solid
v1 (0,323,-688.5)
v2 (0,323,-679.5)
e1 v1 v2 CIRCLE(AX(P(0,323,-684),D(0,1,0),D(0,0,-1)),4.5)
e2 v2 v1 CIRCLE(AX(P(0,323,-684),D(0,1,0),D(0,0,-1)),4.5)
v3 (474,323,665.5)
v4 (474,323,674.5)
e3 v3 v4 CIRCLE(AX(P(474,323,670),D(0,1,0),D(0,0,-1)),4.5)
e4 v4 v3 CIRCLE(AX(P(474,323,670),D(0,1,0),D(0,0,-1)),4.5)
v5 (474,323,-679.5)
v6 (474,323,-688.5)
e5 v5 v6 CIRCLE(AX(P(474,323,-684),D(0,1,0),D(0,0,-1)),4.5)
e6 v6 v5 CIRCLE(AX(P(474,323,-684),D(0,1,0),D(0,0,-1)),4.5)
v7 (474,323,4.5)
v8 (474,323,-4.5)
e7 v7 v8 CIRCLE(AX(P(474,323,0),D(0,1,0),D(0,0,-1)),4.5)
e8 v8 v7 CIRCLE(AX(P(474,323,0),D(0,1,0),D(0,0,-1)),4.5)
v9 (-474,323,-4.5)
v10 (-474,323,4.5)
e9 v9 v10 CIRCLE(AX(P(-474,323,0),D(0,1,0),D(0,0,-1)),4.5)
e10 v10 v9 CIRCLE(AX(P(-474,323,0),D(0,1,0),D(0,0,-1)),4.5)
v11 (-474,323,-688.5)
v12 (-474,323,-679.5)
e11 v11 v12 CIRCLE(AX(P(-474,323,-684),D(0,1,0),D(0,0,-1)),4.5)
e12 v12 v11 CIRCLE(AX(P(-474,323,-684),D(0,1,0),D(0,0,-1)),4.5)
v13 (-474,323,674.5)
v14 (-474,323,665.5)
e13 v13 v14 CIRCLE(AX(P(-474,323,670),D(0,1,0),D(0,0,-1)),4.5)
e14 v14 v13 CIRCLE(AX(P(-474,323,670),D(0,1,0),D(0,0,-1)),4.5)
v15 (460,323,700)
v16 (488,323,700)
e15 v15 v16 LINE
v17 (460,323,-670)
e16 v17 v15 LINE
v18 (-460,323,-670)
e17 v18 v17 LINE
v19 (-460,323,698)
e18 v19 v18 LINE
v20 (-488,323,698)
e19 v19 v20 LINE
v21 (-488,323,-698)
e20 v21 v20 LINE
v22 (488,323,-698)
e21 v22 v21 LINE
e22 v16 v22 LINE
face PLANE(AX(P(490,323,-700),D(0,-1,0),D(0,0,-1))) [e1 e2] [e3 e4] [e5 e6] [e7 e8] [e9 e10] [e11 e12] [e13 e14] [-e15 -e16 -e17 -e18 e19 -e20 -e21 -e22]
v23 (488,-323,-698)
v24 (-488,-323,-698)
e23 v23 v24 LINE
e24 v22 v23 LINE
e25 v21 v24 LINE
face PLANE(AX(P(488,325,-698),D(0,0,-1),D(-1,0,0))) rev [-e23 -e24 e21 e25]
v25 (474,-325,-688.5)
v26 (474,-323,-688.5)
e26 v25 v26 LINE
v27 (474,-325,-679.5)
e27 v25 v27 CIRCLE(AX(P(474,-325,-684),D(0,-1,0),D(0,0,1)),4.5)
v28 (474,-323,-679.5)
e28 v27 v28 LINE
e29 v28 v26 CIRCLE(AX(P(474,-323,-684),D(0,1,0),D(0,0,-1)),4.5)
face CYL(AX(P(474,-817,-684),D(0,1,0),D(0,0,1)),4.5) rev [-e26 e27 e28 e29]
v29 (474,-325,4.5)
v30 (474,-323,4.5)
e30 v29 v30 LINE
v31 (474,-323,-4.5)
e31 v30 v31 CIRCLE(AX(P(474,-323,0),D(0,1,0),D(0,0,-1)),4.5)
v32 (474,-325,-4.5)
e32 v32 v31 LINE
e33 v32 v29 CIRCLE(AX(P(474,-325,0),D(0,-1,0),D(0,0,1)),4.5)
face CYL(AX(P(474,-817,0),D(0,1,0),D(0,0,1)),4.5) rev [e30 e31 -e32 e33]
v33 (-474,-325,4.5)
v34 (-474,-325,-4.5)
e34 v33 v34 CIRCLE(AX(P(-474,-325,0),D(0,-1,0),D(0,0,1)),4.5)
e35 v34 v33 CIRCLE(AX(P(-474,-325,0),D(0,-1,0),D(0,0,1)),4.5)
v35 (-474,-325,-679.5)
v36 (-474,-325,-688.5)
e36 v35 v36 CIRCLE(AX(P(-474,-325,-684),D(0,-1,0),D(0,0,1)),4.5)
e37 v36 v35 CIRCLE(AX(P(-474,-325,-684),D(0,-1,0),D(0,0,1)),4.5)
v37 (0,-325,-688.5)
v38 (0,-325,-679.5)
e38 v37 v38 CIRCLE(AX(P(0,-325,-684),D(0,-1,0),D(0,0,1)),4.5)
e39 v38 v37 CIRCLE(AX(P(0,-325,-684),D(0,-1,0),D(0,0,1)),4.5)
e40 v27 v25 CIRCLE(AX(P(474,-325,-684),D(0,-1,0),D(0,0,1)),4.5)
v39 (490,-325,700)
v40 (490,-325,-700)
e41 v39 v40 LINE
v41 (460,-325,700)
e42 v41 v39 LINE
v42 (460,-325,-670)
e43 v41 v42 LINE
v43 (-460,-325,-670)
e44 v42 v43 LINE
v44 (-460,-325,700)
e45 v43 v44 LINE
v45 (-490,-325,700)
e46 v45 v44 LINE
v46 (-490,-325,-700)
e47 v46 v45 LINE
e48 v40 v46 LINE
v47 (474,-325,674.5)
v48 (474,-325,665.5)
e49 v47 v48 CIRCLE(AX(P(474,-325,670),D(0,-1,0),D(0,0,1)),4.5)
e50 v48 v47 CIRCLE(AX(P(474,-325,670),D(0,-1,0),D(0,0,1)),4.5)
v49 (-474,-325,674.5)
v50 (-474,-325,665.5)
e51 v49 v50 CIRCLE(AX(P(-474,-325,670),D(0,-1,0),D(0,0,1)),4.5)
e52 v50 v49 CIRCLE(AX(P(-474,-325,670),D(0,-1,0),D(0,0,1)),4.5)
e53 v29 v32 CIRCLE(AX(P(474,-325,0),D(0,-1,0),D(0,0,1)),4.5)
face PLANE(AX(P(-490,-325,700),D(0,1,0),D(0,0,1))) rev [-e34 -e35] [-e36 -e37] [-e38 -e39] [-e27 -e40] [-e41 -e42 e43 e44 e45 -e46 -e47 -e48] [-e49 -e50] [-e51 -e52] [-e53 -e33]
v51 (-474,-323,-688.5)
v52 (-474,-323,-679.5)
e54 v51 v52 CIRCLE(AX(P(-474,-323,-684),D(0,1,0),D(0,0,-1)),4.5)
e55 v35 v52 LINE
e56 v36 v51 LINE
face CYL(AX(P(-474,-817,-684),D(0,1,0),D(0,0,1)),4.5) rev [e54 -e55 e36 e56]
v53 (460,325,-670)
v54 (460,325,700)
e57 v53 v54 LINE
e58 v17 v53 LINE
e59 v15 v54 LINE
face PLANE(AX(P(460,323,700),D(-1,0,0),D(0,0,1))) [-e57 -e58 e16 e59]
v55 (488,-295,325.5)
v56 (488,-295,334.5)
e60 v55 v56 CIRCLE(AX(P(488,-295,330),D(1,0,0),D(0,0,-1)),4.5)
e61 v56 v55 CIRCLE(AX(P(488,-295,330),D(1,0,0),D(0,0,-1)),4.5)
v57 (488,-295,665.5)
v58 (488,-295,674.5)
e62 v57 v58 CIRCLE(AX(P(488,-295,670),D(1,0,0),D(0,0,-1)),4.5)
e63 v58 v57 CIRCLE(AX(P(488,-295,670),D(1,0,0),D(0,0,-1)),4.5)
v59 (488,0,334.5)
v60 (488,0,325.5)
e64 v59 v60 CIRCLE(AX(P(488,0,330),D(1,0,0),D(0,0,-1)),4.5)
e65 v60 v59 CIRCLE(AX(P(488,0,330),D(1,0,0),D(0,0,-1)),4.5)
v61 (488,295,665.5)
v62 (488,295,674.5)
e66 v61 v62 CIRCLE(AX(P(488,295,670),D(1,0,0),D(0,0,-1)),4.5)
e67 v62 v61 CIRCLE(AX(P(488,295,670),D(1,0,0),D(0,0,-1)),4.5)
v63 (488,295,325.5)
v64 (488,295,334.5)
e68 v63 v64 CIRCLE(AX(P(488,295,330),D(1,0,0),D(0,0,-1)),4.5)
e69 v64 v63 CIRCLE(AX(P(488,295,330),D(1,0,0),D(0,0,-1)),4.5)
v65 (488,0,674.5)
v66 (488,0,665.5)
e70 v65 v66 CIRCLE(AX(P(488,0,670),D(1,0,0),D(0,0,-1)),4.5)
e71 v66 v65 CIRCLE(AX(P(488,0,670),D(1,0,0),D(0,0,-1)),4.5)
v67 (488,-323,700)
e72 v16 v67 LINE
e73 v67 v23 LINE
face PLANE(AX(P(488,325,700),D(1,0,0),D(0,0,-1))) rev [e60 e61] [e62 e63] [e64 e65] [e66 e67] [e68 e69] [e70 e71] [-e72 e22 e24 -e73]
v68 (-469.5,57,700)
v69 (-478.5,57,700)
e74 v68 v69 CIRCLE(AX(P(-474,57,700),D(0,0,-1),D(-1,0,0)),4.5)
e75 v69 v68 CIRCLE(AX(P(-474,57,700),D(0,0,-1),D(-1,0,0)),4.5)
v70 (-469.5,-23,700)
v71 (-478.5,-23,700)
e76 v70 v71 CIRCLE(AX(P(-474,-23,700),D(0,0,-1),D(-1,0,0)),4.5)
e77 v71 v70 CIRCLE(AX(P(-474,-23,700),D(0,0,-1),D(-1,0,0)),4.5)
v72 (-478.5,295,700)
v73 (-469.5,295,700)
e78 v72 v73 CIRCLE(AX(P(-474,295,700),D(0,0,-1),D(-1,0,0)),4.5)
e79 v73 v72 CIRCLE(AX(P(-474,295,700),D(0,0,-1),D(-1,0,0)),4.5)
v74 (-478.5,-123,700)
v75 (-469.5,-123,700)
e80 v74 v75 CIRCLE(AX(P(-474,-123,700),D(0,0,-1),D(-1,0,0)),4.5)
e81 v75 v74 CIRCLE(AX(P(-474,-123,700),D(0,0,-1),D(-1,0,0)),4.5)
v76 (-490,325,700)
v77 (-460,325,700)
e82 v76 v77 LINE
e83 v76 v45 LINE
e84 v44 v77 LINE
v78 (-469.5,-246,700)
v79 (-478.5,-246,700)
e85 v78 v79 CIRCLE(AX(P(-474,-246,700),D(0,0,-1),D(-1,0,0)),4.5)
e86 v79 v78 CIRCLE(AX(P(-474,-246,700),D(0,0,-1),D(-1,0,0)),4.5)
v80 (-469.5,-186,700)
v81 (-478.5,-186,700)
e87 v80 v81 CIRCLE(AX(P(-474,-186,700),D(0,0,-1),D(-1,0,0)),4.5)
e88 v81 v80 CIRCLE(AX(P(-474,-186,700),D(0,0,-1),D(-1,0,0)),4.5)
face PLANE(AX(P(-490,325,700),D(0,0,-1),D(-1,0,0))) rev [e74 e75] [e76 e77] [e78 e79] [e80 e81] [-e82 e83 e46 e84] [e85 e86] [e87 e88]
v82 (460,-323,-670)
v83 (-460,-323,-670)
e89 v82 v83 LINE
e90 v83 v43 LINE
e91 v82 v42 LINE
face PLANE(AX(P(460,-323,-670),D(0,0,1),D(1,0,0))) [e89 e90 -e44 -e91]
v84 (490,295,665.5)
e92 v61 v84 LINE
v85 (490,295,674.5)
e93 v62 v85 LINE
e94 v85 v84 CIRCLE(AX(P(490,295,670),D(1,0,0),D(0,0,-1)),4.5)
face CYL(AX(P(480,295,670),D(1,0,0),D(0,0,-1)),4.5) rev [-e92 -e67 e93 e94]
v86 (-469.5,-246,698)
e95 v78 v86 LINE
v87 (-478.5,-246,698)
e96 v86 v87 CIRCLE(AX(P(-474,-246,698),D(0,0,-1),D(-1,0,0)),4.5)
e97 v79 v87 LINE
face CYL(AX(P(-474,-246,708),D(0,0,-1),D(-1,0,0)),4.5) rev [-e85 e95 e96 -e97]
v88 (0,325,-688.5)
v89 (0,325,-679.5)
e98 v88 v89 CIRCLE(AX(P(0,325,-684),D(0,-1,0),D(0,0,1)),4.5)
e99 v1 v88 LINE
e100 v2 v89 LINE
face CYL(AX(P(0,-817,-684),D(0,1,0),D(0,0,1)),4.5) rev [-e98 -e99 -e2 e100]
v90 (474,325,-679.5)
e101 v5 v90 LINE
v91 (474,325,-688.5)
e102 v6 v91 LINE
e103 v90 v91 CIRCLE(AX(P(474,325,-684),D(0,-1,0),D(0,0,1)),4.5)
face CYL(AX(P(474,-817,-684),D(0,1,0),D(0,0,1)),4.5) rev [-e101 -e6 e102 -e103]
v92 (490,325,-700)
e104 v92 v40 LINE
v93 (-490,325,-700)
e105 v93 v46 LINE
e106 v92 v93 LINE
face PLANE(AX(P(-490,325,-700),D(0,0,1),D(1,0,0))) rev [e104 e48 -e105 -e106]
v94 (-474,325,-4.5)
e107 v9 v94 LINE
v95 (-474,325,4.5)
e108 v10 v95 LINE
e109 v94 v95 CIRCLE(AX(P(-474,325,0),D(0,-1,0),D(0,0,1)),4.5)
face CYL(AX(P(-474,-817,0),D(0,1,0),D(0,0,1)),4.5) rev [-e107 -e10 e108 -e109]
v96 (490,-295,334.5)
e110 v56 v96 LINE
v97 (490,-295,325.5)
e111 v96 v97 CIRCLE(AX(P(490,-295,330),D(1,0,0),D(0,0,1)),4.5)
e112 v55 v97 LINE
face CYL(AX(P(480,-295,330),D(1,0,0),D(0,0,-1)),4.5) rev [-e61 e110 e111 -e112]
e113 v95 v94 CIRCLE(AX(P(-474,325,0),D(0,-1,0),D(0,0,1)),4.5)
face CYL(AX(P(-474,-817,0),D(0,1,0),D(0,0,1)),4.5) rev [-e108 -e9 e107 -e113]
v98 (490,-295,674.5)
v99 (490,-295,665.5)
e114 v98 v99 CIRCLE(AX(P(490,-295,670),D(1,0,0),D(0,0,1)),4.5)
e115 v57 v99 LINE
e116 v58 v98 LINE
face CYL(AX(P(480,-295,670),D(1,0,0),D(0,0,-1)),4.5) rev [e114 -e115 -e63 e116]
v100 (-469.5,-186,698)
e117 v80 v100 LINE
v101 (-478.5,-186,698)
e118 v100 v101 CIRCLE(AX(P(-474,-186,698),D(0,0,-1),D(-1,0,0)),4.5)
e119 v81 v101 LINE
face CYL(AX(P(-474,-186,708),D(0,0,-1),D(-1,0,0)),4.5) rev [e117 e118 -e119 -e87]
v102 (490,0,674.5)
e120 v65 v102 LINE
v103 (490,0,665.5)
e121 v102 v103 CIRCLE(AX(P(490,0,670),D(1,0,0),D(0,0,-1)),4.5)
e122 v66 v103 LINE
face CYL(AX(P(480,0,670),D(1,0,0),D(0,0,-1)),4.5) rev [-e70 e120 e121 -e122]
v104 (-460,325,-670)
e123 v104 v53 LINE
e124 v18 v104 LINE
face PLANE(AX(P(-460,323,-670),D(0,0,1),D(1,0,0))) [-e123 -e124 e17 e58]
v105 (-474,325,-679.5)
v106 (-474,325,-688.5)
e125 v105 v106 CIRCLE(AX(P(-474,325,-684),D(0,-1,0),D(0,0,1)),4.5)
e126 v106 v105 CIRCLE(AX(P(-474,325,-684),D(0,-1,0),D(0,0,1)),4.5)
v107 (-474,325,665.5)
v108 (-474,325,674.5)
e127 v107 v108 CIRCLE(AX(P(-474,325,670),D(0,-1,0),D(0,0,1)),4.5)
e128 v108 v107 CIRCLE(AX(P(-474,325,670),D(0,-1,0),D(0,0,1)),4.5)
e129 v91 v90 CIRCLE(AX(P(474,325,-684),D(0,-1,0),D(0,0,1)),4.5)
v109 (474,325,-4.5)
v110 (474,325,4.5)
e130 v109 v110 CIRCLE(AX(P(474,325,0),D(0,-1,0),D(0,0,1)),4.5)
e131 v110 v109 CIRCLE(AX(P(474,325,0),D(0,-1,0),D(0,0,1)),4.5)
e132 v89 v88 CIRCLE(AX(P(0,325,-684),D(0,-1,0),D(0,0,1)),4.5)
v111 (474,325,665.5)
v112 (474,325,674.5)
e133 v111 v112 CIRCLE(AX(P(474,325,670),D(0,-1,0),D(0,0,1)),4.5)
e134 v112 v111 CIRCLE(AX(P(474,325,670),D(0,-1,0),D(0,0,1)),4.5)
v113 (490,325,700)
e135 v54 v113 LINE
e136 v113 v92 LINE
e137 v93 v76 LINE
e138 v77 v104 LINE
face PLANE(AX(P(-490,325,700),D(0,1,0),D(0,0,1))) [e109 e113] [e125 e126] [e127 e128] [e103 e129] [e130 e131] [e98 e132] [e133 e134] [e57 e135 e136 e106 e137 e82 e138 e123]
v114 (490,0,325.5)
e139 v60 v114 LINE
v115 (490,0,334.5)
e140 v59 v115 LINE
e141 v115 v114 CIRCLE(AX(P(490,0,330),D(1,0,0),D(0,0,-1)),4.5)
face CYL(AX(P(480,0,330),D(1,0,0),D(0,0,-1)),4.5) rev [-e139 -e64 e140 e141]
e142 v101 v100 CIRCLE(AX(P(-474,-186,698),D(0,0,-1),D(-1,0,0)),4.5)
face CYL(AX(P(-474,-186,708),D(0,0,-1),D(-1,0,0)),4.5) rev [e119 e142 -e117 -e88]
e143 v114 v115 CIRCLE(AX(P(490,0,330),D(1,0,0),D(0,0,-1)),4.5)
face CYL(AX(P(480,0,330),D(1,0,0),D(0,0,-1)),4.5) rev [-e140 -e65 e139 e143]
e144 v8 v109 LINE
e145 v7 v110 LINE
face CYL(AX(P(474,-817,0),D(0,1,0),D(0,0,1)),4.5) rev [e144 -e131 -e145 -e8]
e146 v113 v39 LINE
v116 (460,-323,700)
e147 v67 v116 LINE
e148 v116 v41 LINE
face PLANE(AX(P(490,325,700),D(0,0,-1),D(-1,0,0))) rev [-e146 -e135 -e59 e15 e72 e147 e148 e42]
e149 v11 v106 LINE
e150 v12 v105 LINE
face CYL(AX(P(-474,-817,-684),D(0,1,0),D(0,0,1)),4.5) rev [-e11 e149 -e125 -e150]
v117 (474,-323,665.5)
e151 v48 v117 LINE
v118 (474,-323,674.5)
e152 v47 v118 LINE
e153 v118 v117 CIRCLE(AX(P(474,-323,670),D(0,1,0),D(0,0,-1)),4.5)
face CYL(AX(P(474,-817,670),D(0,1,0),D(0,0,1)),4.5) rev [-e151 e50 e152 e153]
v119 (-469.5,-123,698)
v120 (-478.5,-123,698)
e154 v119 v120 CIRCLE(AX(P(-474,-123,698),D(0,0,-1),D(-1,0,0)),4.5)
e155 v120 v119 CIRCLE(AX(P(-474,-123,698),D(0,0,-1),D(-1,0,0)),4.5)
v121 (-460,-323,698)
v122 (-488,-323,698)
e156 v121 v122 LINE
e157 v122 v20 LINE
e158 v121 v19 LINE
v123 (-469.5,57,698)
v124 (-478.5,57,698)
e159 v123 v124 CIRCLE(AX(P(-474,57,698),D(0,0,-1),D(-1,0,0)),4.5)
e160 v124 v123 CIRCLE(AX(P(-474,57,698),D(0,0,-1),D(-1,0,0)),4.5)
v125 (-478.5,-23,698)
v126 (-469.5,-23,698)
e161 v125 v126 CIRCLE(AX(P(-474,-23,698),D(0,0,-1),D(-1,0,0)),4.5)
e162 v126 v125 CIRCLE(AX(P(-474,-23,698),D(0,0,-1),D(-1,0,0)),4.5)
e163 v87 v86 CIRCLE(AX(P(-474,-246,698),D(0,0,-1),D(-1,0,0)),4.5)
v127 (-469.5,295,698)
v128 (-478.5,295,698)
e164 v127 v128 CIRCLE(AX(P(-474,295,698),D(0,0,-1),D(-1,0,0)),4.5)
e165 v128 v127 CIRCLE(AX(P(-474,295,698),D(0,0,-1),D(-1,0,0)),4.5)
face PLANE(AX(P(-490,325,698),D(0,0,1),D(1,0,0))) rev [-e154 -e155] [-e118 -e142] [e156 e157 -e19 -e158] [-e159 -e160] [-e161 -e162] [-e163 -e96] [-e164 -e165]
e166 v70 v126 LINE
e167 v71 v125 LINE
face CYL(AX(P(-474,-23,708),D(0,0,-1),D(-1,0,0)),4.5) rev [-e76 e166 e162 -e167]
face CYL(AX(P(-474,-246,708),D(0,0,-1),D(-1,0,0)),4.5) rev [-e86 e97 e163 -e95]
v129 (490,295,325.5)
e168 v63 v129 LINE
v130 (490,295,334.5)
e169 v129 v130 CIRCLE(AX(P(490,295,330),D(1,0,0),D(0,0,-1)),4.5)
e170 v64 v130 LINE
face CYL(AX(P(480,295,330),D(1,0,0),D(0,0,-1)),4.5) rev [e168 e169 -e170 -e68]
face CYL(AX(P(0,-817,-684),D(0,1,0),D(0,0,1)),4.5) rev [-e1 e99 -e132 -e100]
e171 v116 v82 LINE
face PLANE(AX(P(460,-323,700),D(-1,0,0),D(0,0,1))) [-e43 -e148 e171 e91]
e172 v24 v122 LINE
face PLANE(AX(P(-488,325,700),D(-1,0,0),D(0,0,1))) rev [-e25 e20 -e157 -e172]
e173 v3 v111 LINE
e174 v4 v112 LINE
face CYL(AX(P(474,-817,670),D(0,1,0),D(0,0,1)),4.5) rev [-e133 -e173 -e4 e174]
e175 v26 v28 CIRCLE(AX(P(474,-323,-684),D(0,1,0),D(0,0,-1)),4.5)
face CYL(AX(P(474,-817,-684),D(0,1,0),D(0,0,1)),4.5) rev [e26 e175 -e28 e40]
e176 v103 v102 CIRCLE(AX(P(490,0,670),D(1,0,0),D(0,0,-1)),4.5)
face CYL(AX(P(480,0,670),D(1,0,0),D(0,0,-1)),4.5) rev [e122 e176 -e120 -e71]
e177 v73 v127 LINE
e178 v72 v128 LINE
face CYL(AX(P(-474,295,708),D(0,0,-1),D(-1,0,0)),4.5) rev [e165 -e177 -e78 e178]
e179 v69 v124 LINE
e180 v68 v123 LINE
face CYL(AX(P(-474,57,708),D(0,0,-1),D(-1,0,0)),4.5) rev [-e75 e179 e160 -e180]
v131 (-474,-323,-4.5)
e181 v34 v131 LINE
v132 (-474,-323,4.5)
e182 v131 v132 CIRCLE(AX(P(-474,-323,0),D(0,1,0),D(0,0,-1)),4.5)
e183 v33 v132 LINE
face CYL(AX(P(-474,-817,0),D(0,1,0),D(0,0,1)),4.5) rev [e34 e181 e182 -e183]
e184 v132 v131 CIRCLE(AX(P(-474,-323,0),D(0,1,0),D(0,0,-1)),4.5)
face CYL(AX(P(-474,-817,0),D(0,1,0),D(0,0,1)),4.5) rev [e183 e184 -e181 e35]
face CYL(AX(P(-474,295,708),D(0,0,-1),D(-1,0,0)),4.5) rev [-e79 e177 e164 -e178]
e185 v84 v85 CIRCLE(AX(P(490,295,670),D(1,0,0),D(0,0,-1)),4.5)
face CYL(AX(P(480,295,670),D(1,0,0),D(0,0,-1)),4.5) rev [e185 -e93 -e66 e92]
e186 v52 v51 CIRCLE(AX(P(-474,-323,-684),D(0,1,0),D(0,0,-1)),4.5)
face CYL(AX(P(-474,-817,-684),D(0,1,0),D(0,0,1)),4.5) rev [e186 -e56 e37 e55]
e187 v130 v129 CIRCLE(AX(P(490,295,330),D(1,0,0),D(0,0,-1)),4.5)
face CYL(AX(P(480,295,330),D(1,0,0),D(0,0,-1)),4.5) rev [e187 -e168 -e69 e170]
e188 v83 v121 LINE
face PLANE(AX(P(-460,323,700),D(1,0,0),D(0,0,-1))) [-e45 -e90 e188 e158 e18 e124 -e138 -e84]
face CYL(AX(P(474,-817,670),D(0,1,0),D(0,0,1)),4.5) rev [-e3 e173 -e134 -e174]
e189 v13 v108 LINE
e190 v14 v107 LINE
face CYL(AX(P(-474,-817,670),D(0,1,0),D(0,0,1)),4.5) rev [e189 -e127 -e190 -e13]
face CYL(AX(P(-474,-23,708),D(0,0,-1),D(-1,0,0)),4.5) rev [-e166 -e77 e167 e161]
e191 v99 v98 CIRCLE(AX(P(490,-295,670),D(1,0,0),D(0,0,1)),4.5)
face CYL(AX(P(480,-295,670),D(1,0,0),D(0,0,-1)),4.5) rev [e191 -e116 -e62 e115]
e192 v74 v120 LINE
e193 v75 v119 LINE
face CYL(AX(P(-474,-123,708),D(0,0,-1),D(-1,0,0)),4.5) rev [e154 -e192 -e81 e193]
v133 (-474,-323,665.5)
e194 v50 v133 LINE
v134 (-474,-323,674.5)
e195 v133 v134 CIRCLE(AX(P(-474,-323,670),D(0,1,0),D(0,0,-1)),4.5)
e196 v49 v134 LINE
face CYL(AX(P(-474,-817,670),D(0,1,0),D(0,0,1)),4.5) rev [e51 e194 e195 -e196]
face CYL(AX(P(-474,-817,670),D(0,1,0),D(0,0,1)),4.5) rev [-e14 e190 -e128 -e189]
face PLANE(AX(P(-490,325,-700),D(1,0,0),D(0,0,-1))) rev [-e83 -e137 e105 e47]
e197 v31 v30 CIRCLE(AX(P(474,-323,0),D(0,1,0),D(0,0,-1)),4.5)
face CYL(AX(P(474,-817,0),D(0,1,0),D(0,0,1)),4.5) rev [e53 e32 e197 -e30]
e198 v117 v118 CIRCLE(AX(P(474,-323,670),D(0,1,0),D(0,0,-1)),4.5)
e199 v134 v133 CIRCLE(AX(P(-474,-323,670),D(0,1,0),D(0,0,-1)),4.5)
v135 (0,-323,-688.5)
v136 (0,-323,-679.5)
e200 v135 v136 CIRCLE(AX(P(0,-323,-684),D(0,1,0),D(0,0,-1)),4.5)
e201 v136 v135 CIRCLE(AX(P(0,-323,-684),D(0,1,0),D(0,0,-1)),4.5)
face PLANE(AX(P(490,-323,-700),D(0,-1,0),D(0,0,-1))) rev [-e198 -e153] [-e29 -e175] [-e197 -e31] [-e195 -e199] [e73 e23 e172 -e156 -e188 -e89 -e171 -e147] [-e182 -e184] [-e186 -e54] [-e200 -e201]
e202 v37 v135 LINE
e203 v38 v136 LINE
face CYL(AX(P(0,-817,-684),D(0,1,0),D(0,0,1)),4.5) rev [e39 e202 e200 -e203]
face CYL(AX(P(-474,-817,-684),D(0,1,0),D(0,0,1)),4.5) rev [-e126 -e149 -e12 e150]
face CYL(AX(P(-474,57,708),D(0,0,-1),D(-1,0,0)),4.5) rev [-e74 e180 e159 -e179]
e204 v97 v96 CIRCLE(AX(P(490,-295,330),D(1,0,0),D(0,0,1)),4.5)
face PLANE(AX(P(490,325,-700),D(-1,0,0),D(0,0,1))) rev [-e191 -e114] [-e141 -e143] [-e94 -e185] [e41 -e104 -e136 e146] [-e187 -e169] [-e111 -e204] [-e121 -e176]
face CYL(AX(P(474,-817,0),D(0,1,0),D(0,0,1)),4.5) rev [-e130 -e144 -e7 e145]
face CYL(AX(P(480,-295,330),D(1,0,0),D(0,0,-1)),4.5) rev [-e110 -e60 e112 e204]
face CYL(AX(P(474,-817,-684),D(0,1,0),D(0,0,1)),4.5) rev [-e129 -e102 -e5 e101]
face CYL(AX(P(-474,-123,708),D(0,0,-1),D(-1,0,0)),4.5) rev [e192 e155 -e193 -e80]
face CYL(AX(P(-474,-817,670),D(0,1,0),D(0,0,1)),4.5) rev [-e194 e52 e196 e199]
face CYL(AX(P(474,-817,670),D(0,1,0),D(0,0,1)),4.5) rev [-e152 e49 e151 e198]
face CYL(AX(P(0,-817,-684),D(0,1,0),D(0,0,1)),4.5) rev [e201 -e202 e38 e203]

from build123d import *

# Parameters (mm, degrees)
EXTRUDE_1_DEPTH          = 325
EXTRUDE_2_DEPTH          = 2
EXTRUDE_3_DEPTH          = 2
SKETCH_5_W               = 30
SKETCH_5_H               = 650
EXTRUDE_4_DEPTH          = 2
SKETCH_6_R               = 4.5
CUT_EXTRUDE_1_DEPTH      = 10
CUT_EXTRUDE_2_DEPTH      = 1140
CUT_EXTRUDE_2_DEPTH_BACK = 345
SKETCH_7_R               = 4.5
SKETCH_8_R               = 4.5
CUT_EXTRUDE_3_DEPTH      = 10


with BuildPart() as part:
    # 草图1 → 凸台-拉伸1 (new, symmetric)
    with BuildSketch(Plane(origin=(0, 0, 0), x_dir=(1, 0, 0), z_dir=(0, 1, 0))):
        Polygon((-490, 700), (490, 700), (490, -700), (488, -700), (488, 698), (-488, 698), (-488, -700), (-490, -700), align=None)
    extrude(amount=EXTRUDE_1_DEPTH, both=True)

    # 草图2 → 凸台-拉伸2 (add)
    with BuildSketch(Plane(origin=(0, 325, 0), x_dir=(1, 0, 0), z_dir=(0, 1, 0))):
        Polygon((-490, 700), (-490, -700), (-460, -700), (-460, 670), (460, 670), (460, -700), (490, -700), (490, 700), align=None)
    extrude(amount=-EXTRUDE_2_DEPTH)

    # 草图3 → 凸台-拉伸3 (add)
    with BuildSketch(Plane.XZ.offset(325)):
        Polygon((490, -700), (490, 700), (460, 700), (460, -670), (-460, -670), (-460, 700), (-490, 700), (-490, -700), align=None)
    extrude(amount=-EXTRUDE_3_DEPTH)

    # 草图5 → 凸台-拉伸4 (add)
    with BuildSketch(Plane.XY.offset(700)):
        with Locations((-475, 0)):
            Rectangle(SKETCH_5_W, SKETCH_5_H)
    extrude(amount=-EXTRUDE_4_DEPTH)

    # 草图6 → 切除-拉伸1 (cut)
    with BuildSketch(Plane(origin=(0, 0, 698), x_dir=(-1, 0, 0), z_dir=(0, 0, -1))):
        with Locations((474, -246)):
            Circle(SKETCH_6_R)
        with Locations((474, -186)):
            Circle(SKETCH_6_R)
        with Locations((474, 295)):
            Circle(SKETCH_6_R)
        with Locations((474, 57)):
            Circle(SKETCH_6_R)
        with Locations((474, -23)):
            Circle(SKETCH_6_R)
        with Locations((474, -123)):
            Circle(SKETCH_6_R)
    extrude(amount=-CUT_EXTRUDE_1_DEPTH, mode=Mode.SUBTRACT)

    # 草图7 → 切除-拉伸2 (cut, two sides: drawn at the far end of the back side and taken through both)
    with BuildSketch(Plane.XZ.offset(-323).offset(-CUT_EXTRUDE_2_DEPTH_BACK)):
        with Locations(Location((-474, 670, 0), (0, 0, 90))):
            Circle(SKETCH_7_R)
        with Locations(Location((-474, 0, 0), (0, 0, 90))):
            Circle(SKETCH_7_R)
        with Locations(Location((-474, -684, 0), (0, 0, 90))):
            Circle(SKETCH_7_R)
        with Locations(Location((474, -684, 0), (0, 0, 90))):
            Circle(SKETCH_7_R)
        with Locations(Location((0, -684, 0), (0, 0, 90))):
            Circle(SKETCH_7_R)
        with Locations(Location((474, 0, 0), (0, 0, 90))):
            Circle(SKETCH_7_R)
        with Locations(Location((474, 670, 0), (0, 0, 90))):
            Circle(SKETCH_7_R)
    extrude(amount=CUT_EXTRUDE_2_DEPTH + CUT_EXTRUDE_2_DEPTH_BACK, mode=Mode.SUBTRACT)

    # 草图8 → 切除-拉伸3 (cut)
    with BuildSketch(Plane(origin=(490, 0, 0), x_dir=(0, 0, -1), z_dir=(1, 0, 0))):
        with Locations((-330, 295)):
            Circle(SKETCH_8_R)
        with Locations((-670, 295)):
            Circle(SKETCH_8_R)
        with Locations((-670, -295)):
            Circle(SKETCH_8_R)
        with Locations((-330, -295)):
            Circle(SKETCH_8_R)
        with Locations((-330, 0)):
            Circle(SKETCH_8_R)
        with Locations((-670, 0)):
            Circle(SKETCH_8_R)
    extrude(amount=-CUT_EXTRUDE_3_DEPTH, mode=Mode.SUBTRACT)


solid = part.part
